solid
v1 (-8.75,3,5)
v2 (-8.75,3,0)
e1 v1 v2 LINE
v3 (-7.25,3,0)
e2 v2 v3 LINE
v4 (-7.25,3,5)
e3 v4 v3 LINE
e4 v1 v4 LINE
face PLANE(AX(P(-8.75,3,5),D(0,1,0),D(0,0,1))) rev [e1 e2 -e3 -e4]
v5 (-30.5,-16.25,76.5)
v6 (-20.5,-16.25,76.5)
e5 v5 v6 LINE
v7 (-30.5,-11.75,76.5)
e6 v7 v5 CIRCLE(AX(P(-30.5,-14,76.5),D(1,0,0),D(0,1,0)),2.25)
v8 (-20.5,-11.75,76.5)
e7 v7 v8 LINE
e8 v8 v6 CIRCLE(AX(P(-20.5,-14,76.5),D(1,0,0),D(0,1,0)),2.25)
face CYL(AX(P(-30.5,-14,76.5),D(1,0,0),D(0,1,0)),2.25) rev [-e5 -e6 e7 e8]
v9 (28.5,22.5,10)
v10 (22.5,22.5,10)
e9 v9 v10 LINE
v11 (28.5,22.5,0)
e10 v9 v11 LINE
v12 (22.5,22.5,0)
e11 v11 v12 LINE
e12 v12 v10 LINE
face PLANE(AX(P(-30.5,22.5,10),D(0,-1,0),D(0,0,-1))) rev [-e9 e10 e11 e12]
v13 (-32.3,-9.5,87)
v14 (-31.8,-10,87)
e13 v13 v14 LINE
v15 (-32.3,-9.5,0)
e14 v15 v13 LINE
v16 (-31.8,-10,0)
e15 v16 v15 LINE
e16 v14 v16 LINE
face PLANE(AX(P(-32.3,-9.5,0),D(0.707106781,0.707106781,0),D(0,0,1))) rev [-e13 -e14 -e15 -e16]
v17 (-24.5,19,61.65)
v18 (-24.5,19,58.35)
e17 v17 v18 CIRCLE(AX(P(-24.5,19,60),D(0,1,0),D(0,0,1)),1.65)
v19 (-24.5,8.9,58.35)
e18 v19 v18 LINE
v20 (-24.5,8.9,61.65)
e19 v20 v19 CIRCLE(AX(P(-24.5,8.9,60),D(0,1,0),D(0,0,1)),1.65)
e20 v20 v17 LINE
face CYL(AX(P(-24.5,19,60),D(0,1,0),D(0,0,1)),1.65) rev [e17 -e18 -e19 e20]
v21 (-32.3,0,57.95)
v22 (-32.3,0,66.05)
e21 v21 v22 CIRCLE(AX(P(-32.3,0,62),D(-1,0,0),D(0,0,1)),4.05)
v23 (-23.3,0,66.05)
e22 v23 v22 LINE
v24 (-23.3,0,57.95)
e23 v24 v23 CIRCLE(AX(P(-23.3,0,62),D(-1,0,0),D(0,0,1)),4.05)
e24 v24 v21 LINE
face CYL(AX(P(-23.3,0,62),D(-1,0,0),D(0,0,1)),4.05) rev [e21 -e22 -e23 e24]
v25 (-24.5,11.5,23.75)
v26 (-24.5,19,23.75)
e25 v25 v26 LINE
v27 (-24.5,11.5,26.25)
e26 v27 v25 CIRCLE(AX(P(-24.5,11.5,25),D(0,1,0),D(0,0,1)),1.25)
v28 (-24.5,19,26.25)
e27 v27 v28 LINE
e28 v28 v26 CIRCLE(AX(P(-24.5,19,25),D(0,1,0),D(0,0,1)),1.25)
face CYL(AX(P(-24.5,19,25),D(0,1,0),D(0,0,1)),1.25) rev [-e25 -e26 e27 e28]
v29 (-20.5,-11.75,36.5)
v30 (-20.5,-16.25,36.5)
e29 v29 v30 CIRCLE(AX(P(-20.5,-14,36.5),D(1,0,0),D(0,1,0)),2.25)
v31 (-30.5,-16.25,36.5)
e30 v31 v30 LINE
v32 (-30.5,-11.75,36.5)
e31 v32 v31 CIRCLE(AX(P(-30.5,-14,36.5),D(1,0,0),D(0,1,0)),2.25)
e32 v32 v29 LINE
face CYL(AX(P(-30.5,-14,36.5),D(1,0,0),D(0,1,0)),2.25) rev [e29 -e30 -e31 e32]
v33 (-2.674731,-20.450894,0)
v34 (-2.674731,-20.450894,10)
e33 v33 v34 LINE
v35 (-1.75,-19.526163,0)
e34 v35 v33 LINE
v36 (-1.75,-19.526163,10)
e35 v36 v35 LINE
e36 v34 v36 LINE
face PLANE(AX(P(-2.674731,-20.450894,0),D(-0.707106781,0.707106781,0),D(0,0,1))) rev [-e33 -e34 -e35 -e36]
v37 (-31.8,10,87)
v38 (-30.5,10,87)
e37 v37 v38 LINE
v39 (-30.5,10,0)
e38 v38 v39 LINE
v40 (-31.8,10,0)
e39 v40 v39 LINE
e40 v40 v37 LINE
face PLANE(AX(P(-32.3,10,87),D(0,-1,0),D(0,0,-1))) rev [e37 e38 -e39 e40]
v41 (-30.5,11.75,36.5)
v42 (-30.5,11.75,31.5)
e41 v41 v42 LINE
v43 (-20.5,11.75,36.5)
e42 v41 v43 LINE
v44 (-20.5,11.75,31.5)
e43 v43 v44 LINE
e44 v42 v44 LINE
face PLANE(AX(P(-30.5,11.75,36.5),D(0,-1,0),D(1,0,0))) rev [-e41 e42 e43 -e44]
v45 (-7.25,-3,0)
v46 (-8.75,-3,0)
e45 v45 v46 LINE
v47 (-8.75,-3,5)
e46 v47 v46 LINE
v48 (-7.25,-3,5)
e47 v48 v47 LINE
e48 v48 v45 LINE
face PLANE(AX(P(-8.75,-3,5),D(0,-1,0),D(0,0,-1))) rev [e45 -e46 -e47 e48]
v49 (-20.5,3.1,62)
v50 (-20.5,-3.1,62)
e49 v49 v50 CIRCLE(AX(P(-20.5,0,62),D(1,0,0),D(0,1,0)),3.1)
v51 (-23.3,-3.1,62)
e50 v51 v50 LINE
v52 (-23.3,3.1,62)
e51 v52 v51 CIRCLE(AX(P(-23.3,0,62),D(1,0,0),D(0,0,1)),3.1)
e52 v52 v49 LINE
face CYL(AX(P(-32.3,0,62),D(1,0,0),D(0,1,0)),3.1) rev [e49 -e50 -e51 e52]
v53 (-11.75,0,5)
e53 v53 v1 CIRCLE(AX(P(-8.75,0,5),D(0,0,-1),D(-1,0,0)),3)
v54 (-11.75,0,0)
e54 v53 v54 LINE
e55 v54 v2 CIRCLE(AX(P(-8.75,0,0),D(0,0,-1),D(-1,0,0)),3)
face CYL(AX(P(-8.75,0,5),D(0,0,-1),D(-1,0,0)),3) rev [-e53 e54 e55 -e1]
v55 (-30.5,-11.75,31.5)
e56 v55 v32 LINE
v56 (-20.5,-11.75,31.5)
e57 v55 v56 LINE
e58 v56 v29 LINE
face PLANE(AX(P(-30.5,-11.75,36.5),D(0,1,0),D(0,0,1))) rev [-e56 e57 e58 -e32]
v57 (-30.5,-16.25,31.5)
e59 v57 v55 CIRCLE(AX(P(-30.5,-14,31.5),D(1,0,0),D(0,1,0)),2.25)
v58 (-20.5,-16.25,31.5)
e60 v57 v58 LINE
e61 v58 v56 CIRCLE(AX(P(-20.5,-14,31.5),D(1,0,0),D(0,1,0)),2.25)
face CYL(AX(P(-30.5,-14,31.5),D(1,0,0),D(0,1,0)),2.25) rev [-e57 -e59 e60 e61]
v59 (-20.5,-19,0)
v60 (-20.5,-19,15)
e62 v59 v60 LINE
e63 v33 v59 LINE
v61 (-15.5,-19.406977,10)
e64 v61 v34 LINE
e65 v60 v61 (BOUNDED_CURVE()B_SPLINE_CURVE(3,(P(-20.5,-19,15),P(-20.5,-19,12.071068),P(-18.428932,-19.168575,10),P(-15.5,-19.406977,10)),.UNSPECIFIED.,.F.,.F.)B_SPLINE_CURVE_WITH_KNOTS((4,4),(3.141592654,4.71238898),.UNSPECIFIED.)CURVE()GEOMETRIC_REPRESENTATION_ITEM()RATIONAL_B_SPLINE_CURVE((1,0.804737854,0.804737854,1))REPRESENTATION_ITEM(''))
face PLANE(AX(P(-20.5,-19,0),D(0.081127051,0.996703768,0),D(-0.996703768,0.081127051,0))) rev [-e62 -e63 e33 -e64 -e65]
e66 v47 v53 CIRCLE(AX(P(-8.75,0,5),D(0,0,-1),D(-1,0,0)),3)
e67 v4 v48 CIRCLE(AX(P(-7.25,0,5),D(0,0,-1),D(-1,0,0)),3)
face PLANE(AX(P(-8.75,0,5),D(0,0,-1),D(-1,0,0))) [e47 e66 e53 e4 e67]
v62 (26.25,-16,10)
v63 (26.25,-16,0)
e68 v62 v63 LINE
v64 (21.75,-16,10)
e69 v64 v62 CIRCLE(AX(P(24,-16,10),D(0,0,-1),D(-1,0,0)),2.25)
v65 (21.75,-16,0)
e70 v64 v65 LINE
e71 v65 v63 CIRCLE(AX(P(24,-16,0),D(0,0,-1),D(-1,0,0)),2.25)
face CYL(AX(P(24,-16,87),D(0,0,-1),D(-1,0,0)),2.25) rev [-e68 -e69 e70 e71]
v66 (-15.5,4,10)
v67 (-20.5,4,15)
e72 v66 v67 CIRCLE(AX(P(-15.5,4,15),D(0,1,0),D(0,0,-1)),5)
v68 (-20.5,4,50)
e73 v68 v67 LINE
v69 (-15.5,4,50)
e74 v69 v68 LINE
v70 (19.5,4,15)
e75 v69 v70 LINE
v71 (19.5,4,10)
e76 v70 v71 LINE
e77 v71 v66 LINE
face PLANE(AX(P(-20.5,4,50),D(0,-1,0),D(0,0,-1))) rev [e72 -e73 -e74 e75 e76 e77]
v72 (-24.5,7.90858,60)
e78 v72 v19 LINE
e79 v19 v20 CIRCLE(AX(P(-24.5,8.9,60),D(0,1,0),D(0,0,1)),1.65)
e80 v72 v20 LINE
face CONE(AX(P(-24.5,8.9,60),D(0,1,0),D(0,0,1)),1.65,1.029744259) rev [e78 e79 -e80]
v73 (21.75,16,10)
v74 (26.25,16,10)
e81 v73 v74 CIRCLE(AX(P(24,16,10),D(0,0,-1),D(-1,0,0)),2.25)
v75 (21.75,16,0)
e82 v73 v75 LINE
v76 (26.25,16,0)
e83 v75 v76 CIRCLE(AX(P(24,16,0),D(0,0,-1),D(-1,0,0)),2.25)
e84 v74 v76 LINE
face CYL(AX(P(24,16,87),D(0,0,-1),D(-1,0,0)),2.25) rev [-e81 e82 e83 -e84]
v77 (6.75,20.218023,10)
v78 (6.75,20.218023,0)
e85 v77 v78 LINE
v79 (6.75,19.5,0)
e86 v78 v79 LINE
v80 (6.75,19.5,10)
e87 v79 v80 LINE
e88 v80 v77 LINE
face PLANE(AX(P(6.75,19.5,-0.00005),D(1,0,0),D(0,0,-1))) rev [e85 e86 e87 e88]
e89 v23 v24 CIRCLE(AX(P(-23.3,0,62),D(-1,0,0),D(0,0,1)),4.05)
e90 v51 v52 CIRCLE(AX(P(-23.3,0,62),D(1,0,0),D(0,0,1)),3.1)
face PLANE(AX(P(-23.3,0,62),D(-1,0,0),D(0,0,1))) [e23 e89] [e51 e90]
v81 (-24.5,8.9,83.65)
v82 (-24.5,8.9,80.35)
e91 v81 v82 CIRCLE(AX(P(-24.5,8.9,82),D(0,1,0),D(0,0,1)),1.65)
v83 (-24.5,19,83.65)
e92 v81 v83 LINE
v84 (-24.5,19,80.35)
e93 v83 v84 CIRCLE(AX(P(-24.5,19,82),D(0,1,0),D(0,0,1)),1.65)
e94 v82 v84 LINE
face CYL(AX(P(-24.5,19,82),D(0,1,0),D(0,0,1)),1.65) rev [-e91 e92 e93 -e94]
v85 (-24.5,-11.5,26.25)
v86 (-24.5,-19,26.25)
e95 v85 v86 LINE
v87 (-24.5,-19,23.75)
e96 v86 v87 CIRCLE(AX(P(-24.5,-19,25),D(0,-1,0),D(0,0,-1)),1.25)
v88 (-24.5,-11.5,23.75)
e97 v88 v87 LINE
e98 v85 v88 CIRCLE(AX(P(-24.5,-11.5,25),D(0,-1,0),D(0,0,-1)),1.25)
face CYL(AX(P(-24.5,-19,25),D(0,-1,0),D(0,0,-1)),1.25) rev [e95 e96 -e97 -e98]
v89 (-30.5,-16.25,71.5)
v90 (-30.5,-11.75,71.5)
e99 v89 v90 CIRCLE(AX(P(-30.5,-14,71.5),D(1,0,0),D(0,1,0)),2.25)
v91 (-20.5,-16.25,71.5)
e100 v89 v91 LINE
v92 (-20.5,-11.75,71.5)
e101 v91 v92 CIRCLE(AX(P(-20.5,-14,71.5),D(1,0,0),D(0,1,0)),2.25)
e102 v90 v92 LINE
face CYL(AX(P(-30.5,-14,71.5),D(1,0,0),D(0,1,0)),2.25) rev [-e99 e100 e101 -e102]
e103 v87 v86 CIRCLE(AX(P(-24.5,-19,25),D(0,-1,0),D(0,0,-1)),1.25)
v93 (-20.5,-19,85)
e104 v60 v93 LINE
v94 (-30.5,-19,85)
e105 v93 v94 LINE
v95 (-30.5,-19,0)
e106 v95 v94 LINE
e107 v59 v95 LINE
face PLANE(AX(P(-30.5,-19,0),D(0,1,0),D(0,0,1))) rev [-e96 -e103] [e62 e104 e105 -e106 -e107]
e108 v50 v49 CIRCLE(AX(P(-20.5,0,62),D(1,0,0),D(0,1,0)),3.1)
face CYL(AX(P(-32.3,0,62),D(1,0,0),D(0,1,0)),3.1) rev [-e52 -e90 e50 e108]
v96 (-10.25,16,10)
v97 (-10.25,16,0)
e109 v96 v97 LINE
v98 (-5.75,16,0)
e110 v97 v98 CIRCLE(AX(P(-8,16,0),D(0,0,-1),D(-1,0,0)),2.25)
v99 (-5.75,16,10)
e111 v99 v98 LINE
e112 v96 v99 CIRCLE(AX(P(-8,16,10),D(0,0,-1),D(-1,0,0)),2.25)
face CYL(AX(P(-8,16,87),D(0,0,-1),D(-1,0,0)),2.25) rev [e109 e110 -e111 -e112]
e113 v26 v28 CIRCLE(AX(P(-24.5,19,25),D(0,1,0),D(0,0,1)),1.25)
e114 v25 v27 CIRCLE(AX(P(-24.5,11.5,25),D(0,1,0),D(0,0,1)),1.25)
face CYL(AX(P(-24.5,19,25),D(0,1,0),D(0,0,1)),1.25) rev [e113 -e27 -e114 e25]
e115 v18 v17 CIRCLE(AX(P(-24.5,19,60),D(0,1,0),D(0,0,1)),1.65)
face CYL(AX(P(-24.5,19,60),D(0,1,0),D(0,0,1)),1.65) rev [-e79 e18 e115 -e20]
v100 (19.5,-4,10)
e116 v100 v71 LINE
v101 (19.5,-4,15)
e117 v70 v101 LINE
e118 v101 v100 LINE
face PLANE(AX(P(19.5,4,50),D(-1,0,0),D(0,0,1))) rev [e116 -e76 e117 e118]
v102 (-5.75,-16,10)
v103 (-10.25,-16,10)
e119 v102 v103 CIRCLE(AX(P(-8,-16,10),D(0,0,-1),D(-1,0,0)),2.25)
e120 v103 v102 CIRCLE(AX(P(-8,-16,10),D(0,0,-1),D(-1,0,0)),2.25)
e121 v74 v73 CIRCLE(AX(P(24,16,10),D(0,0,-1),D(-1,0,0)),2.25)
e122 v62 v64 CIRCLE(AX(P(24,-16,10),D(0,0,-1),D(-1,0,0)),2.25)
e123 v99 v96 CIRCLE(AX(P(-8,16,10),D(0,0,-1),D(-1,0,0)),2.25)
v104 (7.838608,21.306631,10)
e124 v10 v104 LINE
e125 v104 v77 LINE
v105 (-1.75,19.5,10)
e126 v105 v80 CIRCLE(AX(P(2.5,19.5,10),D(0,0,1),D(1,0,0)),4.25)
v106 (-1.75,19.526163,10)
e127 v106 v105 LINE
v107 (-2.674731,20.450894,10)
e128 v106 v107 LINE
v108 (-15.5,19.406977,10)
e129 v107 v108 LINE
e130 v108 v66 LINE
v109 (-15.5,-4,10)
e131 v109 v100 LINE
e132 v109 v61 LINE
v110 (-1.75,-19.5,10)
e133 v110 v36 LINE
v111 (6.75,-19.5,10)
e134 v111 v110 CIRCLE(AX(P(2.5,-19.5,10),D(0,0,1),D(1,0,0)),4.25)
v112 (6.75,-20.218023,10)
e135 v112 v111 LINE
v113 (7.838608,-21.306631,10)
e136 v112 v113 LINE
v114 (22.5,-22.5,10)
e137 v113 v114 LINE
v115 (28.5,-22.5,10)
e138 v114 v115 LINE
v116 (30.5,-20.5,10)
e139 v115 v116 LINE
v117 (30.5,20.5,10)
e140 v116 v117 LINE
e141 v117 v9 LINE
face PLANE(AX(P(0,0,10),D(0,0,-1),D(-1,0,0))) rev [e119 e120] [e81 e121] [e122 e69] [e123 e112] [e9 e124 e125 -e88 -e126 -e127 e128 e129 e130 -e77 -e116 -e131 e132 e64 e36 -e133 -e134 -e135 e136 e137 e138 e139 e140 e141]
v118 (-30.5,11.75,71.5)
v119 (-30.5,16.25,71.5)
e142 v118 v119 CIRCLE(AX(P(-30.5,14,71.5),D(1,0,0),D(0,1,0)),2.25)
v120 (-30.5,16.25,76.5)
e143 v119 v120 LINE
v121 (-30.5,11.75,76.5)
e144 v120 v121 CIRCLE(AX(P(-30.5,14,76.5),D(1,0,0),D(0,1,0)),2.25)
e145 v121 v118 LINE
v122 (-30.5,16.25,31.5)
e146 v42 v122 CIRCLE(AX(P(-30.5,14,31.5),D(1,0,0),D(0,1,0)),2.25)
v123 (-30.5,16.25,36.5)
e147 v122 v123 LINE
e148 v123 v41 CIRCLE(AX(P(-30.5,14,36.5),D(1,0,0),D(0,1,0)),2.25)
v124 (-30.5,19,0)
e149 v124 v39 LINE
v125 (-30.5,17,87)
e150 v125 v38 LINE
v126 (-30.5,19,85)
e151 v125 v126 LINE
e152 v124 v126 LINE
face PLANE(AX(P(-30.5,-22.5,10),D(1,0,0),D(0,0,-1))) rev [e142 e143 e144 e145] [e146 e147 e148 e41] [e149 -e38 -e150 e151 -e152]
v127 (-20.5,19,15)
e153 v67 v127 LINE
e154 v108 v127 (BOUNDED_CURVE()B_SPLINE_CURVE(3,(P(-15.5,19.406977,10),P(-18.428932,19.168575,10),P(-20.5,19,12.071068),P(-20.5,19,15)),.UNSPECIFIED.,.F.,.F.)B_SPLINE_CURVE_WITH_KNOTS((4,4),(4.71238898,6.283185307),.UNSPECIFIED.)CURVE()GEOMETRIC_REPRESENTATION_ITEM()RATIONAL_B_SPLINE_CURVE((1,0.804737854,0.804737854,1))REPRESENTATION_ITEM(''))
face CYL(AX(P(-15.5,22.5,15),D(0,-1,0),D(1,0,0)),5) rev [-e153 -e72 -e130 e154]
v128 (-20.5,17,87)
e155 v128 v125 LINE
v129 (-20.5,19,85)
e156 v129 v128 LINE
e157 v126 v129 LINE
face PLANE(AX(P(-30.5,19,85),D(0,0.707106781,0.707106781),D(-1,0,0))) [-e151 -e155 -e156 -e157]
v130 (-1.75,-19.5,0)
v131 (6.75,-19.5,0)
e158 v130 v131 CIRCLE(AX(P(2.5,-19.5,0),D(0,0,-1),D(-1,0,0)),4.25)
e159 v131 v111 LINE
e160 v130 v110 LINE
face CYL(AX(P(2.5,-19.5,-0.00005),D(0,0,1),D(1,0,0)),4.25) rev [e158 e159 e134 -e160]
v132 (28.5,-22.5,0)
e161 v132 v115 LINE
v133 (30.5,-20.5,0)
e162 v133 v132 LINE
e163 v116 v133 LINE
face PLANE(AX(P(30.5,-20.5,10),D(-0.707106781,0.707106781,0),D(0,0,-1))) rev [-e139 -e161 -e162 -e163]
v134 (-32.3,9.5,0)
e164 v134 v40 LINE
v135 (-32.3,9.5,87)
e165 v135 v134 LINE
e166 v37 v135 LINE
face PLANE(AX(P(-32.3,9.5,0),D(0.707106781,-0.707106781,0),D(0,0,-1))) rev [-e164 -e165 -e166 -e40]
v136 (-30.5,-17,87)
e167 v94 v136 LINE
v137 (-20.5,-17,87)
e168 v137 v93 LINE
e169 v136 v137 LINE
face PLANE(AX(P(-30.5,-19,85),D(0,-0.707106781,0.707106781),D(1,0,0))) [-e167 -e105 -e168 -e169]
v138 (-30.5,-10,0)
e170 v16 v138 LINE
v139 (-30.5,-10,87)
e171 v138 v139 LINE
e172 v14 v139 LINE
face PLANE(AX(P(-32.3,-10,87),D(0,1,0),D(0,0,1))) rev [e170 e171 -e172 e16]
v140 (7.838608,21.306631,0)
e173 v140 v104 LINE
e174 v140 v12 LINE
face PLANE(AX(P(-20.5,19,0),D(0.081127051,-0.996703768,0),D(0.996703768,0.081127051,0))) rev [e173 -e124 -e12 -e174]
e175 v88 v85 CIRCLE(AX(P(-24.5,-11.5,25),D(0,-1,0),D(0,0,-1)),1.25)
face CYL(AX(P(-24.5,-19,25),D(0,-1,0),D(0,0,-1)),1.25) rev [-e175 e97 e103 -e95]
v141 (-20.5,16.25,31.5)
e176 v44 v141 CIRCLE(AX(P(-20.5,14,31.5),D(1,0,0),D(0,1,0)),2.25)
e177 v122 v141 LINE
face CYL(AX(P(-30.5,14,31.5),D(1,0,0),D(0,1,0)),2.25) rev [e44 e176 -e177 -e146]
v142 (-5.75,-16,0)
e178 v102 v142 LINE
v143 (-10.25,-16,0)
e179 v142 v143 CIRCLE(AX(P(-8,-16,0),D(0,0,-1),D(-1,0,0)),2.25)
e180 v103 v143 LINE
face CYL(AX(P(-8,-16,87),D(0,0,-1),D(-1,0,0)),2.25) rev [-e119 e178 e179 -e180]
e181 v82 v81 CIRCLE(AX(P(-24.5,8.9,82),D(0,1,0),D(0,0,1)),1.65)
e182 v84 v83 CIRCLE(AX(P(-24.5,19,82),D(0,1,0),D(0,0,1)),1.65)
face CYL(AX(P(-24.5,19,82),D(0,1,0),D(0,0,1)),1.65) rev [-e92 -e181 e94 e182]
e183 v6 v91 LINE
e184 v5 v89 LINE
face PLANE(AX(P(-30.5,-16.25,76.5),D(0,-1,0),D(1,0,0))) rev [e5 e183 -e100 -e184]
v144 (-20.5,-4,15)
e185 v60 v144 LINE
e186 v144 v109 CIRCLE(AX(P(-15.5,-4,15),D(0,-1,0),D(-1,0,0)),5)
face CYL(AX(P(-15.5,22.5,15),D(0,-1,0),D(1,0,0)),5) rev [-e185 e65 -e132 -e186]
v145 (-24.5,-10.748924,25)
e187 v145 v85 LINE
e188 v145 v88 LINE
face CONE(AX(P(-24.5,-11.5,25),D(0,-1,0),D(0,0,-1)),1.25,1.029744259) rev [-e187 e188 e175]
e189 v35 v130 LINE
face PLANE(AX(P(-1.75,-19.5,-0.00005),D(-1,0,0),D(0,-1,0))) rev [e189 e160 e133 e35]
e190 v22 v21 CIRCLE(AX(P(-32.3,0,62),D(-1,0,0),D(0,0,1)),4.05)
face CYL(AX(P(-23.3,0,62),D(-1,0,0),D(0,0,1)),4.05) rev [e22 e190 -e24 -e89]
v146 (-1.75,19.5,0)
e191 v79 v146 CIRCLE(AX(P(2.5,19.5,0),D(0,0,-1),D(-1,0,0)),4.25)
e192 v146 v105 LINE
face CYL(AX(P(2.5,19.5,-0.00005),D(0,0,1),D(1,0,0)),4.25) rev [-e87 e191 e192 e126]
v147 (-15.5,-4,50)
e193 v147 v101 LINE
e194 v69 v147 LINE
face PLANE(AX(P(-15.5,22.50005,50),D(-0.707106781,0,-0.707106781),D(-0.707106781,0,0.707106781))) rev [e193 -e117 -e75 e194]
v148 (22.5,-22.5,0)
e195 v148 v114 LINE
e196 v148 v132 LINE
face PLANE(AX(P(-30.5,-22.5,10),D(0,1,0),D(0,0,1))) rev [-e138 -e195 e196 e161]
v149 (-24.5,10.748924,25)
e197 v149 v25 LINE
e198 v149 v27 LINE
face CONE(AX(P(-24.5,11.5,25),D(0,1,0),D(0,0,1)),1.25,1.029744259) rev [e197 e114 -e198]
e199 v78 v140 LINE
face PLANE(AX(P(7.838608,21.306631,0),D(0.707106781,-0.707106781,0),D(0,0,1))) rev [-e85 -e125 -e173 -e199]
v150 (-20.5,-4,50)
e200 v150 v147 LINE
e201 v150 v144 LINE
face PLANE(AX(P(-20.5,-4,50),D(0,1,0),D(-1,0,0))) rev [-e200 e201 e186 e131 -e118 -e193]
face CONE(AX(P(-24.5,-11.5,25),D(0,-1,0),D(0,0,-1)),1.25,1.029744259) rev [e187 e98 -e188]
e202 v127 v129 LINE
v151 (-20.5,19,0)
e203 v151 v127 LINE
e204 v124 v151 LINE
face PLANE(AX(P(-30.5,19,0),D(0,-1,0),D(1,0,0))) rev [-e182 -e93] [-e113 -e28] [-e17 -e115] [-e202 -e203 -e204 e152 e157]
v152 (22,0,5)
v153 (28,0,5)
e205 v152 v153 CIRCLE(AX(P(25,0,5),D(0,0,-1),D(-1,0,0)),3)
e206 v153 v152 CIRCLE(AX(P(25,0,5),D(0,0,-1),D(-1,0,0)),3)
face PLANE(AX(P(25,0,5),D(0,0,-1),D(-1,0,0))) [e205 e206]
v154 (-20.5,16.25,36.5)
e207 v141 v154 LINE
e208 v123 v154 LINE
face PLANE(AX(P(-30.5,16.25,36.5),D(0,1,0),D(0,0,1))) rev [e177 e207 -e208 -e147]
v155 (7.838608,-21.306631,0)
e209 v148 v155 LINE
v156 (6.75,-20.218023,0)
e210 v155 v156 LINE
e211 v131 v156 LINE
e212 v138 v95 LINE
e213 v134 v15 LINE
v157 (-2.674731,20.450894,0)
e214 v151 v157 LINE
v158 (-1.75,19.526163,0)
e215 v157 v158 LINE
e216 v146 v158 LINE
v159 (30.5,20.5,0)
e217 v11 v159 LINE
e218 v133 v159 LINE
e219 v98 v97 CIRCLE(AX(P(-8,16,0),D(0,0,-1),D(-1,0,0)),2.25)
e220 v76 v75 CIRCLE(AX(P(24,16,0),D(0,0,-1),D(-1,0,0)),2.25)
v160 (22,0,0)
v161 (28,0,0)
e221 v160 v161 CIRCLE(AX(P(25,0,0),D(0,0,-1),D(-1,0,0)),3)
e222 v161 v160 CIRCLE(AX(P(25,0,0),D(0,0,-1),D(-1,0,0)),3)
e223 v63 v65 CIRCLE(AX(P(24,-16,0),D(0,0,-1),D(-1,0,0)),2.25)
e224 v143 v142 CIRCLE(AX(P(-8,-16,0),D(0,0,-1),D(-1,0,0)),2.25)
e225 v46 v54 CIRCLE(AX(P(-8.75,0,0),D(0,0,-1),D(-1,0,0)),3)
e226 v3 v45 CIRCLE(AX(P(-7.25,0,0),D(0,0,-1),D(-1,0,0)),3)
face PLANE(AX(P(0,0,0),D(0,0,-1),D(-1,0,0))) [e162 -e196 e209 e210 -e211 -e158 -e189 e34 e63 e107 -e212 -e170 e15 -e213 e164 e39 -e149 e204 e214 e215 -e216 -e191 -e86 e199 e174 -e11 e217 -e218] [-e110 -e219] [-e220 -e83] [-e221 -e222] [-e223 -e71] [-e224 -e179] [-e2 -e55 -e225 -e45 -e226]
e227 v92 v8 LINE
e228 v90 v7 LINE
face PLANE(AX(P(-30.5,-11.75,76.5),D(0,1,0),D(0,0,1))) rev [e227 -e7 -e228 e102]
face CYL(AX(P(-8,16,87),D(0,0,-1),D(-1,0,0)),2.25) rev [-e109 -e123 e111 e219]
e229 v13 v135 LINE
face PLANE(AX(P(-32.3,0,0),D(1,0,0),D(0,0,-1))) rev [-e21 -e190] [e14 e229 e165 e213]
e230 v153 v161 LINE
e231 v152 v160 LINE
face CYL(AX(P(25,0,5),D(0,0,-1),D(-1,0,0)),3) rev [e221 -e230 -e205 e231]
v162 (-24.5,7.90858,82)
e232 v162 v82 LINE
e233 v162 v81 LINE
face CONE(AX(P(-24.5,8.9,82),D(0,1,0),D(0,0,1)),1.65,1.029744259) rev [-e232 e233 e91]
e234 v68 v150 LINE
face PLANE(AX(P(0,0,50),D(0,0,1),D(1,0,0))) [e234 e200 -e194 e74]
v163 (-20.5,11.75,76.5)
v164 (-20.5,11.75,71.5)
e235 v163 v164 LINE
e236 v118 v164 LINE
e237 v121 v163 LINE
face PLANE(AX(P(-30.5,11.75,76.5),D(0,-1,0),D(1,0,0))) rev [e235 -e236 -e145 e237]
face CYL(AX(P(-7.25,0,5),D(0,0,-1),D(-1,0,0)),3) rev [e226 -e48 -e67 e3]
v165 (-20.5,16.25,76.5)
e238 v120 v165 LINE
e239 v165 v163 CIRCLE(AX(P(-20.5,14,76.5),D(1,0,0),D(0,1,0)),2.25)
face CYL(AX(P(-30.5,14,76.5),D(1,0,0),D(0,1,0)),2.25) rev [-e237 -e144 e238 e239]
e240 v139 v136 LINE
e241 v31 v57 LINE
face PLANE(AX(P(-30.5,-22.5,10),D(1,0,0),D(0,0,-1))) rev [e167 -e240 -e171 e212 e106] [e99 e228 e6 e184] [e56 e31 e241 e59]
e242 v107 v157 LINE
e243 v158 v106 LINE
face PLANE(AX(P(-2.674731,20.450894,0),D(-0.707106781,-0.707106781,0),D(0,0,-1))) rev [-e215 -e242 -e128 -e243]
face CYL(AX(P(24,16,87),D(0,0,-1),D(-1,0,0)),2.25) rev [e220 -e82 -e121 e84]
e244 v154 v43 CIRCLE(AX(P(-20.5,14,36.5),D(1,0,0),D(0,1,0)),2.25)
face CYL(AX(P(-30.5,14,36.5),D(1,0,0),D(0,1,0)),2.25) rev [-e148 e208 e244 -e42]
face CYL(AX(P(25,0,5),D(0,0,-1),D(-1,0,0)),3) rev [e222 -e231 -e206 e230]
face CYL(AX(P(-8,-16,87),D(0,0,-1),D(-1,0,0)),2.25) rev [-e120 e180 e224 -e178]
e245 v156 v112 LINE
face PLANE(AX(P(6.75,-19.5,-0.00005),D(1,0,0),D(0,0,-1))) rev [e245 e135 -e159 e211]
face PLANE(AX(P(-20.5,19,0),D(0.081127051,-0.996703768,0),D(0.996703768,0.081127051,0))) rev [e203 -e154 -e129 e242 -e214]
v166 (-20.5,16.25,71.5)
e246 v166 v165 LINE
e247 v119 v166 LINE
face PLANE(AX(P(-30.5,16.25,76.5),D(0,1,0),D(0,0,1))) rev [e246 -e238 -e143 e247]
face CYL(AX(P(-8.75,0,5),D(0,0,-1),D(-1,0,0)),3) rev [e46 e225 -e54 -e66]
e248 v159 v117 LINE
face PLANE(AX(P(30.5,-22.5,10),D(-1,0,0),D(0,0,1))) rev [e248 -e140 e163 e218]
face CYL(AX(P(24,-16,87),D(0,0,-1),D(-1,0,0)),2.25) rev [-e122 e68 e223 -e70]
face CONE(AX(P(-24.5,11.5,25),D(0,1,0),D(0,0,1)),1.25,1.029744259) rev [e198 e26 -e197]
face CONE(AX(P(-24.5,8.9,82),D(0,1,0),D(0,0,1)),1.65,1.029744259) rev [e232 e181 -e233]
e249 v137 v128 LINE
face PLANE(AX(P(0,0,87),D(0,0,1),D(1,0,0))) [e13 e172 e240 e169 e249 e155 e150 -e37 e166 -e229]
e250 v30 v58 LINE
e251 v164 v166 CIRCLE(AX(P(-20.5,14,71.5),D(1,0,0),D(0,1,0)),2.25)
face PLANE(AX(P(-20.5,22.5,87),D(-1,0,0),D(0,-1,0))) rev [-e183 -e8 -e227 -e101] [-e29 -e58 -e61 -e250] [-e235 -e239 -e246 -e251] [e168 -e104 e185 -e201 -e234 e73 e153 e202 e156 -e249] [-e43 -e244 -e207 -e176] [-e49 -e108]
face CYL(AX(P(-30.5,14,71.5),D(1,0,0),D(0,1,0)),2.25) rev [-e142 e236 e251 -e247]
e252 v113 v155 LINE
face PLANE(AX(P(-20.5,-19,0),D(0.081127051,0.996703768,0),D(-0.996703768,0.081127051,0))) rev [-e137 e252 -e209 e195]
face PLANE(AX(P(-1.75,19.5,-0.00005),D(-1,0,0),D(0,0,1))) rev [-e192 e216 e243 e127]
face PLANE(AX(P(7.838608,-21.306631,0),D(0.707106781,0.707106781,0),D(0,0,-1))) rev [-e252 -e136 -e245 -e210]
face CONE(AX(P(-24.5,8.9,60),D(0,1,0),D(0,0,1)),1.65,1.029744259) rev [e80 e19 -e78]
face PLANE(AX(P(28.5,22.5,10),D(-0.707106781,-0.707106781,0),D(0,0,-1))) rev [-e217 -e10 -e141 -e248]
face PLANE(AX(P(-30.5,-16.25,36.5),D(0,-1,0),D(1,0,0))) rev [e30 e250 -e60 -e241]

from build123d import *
from OCP.BRepFilletAPI import BRepFilletAPI_MakeChamfer

# Parameters (mm, degrees)
SKETCH1_W             = 61
SKETCH1_H             = 45
BOSS_EXTRUDE1_DEPTH   = 10
SKETCH2_W             = 10
SKETCH2_H             = 45
BOSS_EXTRUDE2_DEPTH   = 77
CUT_EXTRUDE3_DEPTH    = 104.325940596
SKETCH6_W             = 40
SKETCH6_H             = 8
BOSS_EXTRUDE3_DEPTH   = 40
CUT_EXTRUDE4_DEPTH    = 96.924449438
FILLET1_R             = 5
CUT_EXTRUDE5_DEPTH    = 95.897312923
LPATTERN2_COUNT       = 2
LPATTERN2_PITCH       = 28
LPATTERN2_COUNT_DIR2  = 2
LPATTERN2_PITCH_DIR2  = 40
SKETCH9_R             = 3
CUT_EXTRUDE6_DEPTH    = 5
SKETCH10_R            = 2.25
CUT_EXTRUDE7_DEPTH    = 95.897312923
CHAMFER1_SIZE         = 2
M4_TAPPED_HOLE1_D     = 3.3
M4_TAPPED_HOLE1_DEPTH = 10.1
M4_TAPPED_HOLE1_TIP   = 0.991420021
SKETCH4_W             = 87
SKETCH4_H             = 20
BOSS_EXTRUDE4_DEPTH   = 1.8
CHAMFER2_SIZE         = 0.5
SKETCH15_R            = 3.1
CUT_EXTRUDE8_DEPTH    = 104.325940596
SKETCH16_R            = 4.05
CUT_EXTRUDE9_DEPTH    = 9
CUT_EXTRUDE10_DEPTH   = 87.478552254
CHAMFER3_SIZE         = 1
CHAMFER3_SIZE2        = 0.927789392
CHAMFER3_SIZE2_2      = 1.092207765


with BuildPart() as part:
    # Sketch1 → Boss-Extrude1 (new body)
    with BuildSketch(Plane.XY):
        Rectangle(SKETCH1_W, SKETCH1_H)
    extrude(amount=BOSS_EXTRUDE1_DEPTH)

    # Sketch2 → Boss-Extrude2 (add)
    with BuildSketch(Plane.XY.offset(10)):
        with Locations((-25.5, 0)):
            Rectangle(SKETCH2_W, SKETCH2_H)
    extrude(amount=BOSS_EXTRUDE2_DEPTH)

    # Sketch5 → Cut-Extrude3 (cut, through all)
    with BuildSketch(Plane(origin=(-20.5, 0, 0), x_dir=(0, 0, -1), z_dir=(1, 0, 0))):
        with BuildLine():
            Line((-76.5, -11.75), (-71.5, -11.75))
            ThreePointArc((-71.5, -11.75), (-69.25, -14), (-71.5, -16.25))
            Line((-71.5, -16.25), (-76.5, -16.25))
            ThreePointArc((-76.5, -16.25), (-78.75, -14), (-76.5, -11.75))
        make_face()
    cut_extrude3 = extrude(amount=-CUT_EXTRUDE3_DEPTH, mode=Mode.SUBTRACT)

    # Sketch6 → Boss-Extrude3 (add)
    with BuildSketch(Plane.XY.offset(10)):
        with Locations((-0.5, 0)):
            Rectangle(SKETCH6_W, SKETCH6_H)
    extrude(amount=BOSS_EXTRUDE3_DEPTH)

    # Sketch7 → Cut-Extrude4 (cut, through all)
    with BuildSketch(Plane.XZ.offset(4)):
        Polygon((19.5, 50), (-15.5, 50), (19.5, 15), align=None)
    extrude(amount=-CUT_EXTRUDE4_DEPTH, mode=Mode.SUBTRACT)

    # Fillet1
    fillet1_edges = [part.edges().sort_by_distance(p)[0] for p in [
        (-20.5, 13.25, 10),
        (-20.5, -13.25, 10),
    ]]
    fillet(fillet1_edges, radius=FILLET1_R)

    # Sketch8 → Cut-Extrude5 (cut, through all)
    with BuildSketch(Plane.XY.offset(87)):
        Polygon((-30.5, 22.5), (22.5, 22.5), (-20.5, 19), (-30.5, 19), align=None)
        Polygon((-20.5, -19), (22.5, -22.5), (-30.5, -22.5), (-30.5, -19), align=None)
    extrude(amount=-CUT_EXTRUDE5_DEPTH, mode=Mode.SUBTRACT)

    # LPattern2: Cut-Extrude3 2 × 2
    with Locations(*[(0, i * LPATTERN2_PITCH, -j * LPATTERN2_PITCH_DIR2) for i in range(LPATTERN2_COUNT) for j in range(LPATTERN2_COUNT_DIR2) if (i, j) != (0, 0)]):
        add(cut_extrude3, mode=Mode.SUBTRACT)

    # Sketch9 → Cut-Extrude6 (cut)
    with BuildSketch(Plane(origin=(0, 0, 0), x_dir=(-1, 0, 0), z_dir=(0, 0, -1))):
        with Locations((-25, 0)):
            Circle(SKETCH9_R)
        with BuildLine():
            Line((8.75, -3), (7.25, -3))
            ThreePointArc((7.25, -3), (4.25, 0), (7.25, 3))
            Line((7.25, 3), (8.75, 3))
            ThreePointArc((8.75, 3), (11.75, 0), (8.75, -3))
        make_face()
    extrude(amount=-CUT_EXTRUDE6_DEPTH, mode=Mode.SUBTRACT)

    # Sketch10 → Cut-Extrude7 (cut, through all)
    with BuildSketch(Plane(origin=(0, 0, 0), x_dir=(-1, 0, 0), z_dir=(0, 0, -1))):
        with Locations((8, -16)):
            Circle(SKETCH10_R)
        with Locations((-24, -16)):
            Circle(SKETCH10_R)
        with Locations((-24, 16)):
            Circle(SKETCH10_R)
        with Locations((8, 16)):
            Circle(SKETCH10_R)
    extrude(amount=-CUT_EXTRUDE7_DEPTH, mode=Mode.SUBTRACT)

    # Chamfer1
    chamfer1_edges = [part.edges().sort_by_distance(p)[0] for p in [
        (30.5, -22.5, 5),
        (30.5, 22.5, 5),
        (-25.5, -19, 87),
        (-25.5, 19, 87),
    ]]
    chamfer(chamfer1_edges, length=CHAMFER1_SIZE)

    # M4 Tapped Hole1
    with Locations(Plane(origin=(0, 19, 0), x_dir=(1, 0, 0), z_dir=(0, 1, 0))):
        with Locations((-24.5, -82), (-24.5, -60)):
            Hole(M4_TAPPED_HOLE1_D / 2, depth=M4_TAPPED_HOLE1_DEPTH)
            with Locations((0, 0, -(M4_TAPPED_HOLE1_DEPTH + M4_TAPPED_HOLE1_TIP / 2))):  # 118° drill point
                Cone(0, M4_TAPPED_HOLE1_D / 2, M4_TAPPED_HOLE1_TIP, mode=Mode.SUBTRACT)

    # Sketch13 → M3 Tapped Hole1 (revolve, cut)
    with BuildSketch(Plane(origin=(-24.5, 19, 25), x_dir=(0, 0, 1), z_dir=(1, 0, 0))):
        Polygon((0, 0), (0, 8.251075774), (1.25, 7.5), (1.25, 0), align=None)
    m3_tapped_hole1 = revolve(axis=Axis((-24.5, 25.35, 25), (0, -1, 0)), mode=Mode.SUBTRACT)

    # Mirror1: M3 Tapped Hole1 across plane
    add(m3_tapped_hole1.mirror(Plane.ZX), mode=Mode.SUBTRACT)

    # Sketch4 → Boss-Extrude4 (add)
    with BuildSketch(Plane.ZY.offset(30.5)):
        with Locations((43.5, 0)):
            Rectangle(SKETCH4_W, SKETCH4_H)
    extrude(amount=BOSS_EXTRUDE4_DEPTH)

    # Chamfer2
    chamfer2_edges = [part.edges().sort_by_distance(p)[0] for p in [
        (-32.3, 10, 43.5),
        (-32.3, -10, 43.5),
    ]]
    chamfer(chamfer2_edges, length=CHAMFER2_SIZE)

    # Sketch15 → Cut-Extrude8 (cut, through all)
    with BuildSketch(Plane(origin=(-20.5, 0, 0), x_dir=(0, 0, -1), z_dir=(1, 0, 0))):
        with Locations(Location((-62, 0, 0), (0, 0, 90))):
            Circle(SKETCH15_R)
    extrude(amount=-CUT_EXTRUDE8_DEPTH, mode=Mode.SUBTRACT)

    # Sketch16 → Cut-Extrude9 (cut)
    with BuildSketch(Plane.ZY.offset(32.3)):
        with Locations((62, 0)):
            Circle(SKETCH16_R)
    extrude(amount=-CUT_EXTRUDE9_DEPTH, mode=Mode.SUBTRACT)

    # Sketch17 → Cut-Extrude10 (cut, through all)
    with BuildSketch(Plane.XY.offset(10)):
        with BuildLine():
            Line((6.75, -19.5), (6.75, -25.912135635))
            ThreePointArc((6.75, -25.912135635), (2.5, -30.162135635), (-1.75, -25.912135635))
            Line((-1.75, -25.912135635), (-1.75, -19.5))
            ThreePointArc((-1.75, -19.5), (2.5, -15.25), (6.75, -19.5))
        make_face()
        with BuildLine():
            Line((-1.75, 19.5), (-1.75, 25.912135635))
            ThreePointArc((-1.75, 25.912135635), (2.5, 30.162135635), (6.75, 25.912135635))
            Line((6.75, 25.912135635), (6.75, 19.5))
            ThreePointArc((6.75, 19.5), (2.5, 15.25), (-1.75, 19.5))
        make_face()
    extrude(amount=-CUT_EXTRUDE10_DEPTH, mode=Mode.SUBTRACT)

    # Chamfer3: one chamfer whose edges measure the first distance from different faces: ONE call of the kernel's chamfer builder (chamfer() names one face for all edges)
    chamfer3_edges_1 = [part.edges().sort_by_distance(p)[0] for p in [
        (-1.75, -20.526162791, 5),
    ]]
    chamfer3_side_1 = [part.faces().sort_by_distance(p)[0] for p in [
        (-1.75, -20.013081395, 5),
    ]]
    chamfer3_edges_2 = [part.edges().sort_by_distance(p)[0] for p in [
        (6.75, -21.218023256, 5),
    ]]
    chamfer3_side_2 = [part.faces().sort_by_distance(p)[0] for p in [
        (6.75, -20.359011628, 5),
    ]]
    chamfer3_edges_3 = [part.edges().sort_by_distance(p)[0] for p in [
        (6.75, 21.218023256, 5),
    ]]
    chamfer3_side_3 = [part.faces().sort_by_distance(p)[0] for p in [
        (6.75, 20.359011628, 5),
    ]]
    chamfer3_edges_4 = [part.edges().sort_by_distance(p)[0] for p in [
        (-1.75, 20.526162791, 5),
    ]]
    chamfer3_side_4 = [part.faces().sort_by_distance(p)[0] for p in [
        (-1.75, 20.013081395, 5),
    ]]
    chamfer3 = BRepFilletAPI_MakeChamfer(part.part.solid().wrapped)
    for e in chamfer3_edges_1:
        chamfer3.Add(CHAMFER3_SIZE, CHAMFER3_SIZE2, e.wrapped, chamfer3_side_1[0].wrapped)  # the first distance lies on this face
    for e in chamfer3_edges_2:
        chamfer3.Add(CHAMFER3_SIZE, CHAMFER3_SIZE2_2, e.wrapped, chamfer3_side_2[0].wrapped)  # the first distance lies on this face
    for e in chamfer3_edges_3:
        chamfer3.Add(CHAMFER3_SIZE, CHAMFER3_SIZE2_2, e.wrapped, chamfer3_side_3[0].wrapped)  # the first distance lies on this face
    for e in chamfer3_edges_4:
        chamfer3.Add(CHAMFER3_SIZE, CHAMFER3_SIZE2, e.wrapped, chamfer3_side_4[0].wrapped)  # the first distance lies on this face
    add(Compound.cast(chamfer3.Shape()), mode=Mode.REPLACE)


solid = part.part
